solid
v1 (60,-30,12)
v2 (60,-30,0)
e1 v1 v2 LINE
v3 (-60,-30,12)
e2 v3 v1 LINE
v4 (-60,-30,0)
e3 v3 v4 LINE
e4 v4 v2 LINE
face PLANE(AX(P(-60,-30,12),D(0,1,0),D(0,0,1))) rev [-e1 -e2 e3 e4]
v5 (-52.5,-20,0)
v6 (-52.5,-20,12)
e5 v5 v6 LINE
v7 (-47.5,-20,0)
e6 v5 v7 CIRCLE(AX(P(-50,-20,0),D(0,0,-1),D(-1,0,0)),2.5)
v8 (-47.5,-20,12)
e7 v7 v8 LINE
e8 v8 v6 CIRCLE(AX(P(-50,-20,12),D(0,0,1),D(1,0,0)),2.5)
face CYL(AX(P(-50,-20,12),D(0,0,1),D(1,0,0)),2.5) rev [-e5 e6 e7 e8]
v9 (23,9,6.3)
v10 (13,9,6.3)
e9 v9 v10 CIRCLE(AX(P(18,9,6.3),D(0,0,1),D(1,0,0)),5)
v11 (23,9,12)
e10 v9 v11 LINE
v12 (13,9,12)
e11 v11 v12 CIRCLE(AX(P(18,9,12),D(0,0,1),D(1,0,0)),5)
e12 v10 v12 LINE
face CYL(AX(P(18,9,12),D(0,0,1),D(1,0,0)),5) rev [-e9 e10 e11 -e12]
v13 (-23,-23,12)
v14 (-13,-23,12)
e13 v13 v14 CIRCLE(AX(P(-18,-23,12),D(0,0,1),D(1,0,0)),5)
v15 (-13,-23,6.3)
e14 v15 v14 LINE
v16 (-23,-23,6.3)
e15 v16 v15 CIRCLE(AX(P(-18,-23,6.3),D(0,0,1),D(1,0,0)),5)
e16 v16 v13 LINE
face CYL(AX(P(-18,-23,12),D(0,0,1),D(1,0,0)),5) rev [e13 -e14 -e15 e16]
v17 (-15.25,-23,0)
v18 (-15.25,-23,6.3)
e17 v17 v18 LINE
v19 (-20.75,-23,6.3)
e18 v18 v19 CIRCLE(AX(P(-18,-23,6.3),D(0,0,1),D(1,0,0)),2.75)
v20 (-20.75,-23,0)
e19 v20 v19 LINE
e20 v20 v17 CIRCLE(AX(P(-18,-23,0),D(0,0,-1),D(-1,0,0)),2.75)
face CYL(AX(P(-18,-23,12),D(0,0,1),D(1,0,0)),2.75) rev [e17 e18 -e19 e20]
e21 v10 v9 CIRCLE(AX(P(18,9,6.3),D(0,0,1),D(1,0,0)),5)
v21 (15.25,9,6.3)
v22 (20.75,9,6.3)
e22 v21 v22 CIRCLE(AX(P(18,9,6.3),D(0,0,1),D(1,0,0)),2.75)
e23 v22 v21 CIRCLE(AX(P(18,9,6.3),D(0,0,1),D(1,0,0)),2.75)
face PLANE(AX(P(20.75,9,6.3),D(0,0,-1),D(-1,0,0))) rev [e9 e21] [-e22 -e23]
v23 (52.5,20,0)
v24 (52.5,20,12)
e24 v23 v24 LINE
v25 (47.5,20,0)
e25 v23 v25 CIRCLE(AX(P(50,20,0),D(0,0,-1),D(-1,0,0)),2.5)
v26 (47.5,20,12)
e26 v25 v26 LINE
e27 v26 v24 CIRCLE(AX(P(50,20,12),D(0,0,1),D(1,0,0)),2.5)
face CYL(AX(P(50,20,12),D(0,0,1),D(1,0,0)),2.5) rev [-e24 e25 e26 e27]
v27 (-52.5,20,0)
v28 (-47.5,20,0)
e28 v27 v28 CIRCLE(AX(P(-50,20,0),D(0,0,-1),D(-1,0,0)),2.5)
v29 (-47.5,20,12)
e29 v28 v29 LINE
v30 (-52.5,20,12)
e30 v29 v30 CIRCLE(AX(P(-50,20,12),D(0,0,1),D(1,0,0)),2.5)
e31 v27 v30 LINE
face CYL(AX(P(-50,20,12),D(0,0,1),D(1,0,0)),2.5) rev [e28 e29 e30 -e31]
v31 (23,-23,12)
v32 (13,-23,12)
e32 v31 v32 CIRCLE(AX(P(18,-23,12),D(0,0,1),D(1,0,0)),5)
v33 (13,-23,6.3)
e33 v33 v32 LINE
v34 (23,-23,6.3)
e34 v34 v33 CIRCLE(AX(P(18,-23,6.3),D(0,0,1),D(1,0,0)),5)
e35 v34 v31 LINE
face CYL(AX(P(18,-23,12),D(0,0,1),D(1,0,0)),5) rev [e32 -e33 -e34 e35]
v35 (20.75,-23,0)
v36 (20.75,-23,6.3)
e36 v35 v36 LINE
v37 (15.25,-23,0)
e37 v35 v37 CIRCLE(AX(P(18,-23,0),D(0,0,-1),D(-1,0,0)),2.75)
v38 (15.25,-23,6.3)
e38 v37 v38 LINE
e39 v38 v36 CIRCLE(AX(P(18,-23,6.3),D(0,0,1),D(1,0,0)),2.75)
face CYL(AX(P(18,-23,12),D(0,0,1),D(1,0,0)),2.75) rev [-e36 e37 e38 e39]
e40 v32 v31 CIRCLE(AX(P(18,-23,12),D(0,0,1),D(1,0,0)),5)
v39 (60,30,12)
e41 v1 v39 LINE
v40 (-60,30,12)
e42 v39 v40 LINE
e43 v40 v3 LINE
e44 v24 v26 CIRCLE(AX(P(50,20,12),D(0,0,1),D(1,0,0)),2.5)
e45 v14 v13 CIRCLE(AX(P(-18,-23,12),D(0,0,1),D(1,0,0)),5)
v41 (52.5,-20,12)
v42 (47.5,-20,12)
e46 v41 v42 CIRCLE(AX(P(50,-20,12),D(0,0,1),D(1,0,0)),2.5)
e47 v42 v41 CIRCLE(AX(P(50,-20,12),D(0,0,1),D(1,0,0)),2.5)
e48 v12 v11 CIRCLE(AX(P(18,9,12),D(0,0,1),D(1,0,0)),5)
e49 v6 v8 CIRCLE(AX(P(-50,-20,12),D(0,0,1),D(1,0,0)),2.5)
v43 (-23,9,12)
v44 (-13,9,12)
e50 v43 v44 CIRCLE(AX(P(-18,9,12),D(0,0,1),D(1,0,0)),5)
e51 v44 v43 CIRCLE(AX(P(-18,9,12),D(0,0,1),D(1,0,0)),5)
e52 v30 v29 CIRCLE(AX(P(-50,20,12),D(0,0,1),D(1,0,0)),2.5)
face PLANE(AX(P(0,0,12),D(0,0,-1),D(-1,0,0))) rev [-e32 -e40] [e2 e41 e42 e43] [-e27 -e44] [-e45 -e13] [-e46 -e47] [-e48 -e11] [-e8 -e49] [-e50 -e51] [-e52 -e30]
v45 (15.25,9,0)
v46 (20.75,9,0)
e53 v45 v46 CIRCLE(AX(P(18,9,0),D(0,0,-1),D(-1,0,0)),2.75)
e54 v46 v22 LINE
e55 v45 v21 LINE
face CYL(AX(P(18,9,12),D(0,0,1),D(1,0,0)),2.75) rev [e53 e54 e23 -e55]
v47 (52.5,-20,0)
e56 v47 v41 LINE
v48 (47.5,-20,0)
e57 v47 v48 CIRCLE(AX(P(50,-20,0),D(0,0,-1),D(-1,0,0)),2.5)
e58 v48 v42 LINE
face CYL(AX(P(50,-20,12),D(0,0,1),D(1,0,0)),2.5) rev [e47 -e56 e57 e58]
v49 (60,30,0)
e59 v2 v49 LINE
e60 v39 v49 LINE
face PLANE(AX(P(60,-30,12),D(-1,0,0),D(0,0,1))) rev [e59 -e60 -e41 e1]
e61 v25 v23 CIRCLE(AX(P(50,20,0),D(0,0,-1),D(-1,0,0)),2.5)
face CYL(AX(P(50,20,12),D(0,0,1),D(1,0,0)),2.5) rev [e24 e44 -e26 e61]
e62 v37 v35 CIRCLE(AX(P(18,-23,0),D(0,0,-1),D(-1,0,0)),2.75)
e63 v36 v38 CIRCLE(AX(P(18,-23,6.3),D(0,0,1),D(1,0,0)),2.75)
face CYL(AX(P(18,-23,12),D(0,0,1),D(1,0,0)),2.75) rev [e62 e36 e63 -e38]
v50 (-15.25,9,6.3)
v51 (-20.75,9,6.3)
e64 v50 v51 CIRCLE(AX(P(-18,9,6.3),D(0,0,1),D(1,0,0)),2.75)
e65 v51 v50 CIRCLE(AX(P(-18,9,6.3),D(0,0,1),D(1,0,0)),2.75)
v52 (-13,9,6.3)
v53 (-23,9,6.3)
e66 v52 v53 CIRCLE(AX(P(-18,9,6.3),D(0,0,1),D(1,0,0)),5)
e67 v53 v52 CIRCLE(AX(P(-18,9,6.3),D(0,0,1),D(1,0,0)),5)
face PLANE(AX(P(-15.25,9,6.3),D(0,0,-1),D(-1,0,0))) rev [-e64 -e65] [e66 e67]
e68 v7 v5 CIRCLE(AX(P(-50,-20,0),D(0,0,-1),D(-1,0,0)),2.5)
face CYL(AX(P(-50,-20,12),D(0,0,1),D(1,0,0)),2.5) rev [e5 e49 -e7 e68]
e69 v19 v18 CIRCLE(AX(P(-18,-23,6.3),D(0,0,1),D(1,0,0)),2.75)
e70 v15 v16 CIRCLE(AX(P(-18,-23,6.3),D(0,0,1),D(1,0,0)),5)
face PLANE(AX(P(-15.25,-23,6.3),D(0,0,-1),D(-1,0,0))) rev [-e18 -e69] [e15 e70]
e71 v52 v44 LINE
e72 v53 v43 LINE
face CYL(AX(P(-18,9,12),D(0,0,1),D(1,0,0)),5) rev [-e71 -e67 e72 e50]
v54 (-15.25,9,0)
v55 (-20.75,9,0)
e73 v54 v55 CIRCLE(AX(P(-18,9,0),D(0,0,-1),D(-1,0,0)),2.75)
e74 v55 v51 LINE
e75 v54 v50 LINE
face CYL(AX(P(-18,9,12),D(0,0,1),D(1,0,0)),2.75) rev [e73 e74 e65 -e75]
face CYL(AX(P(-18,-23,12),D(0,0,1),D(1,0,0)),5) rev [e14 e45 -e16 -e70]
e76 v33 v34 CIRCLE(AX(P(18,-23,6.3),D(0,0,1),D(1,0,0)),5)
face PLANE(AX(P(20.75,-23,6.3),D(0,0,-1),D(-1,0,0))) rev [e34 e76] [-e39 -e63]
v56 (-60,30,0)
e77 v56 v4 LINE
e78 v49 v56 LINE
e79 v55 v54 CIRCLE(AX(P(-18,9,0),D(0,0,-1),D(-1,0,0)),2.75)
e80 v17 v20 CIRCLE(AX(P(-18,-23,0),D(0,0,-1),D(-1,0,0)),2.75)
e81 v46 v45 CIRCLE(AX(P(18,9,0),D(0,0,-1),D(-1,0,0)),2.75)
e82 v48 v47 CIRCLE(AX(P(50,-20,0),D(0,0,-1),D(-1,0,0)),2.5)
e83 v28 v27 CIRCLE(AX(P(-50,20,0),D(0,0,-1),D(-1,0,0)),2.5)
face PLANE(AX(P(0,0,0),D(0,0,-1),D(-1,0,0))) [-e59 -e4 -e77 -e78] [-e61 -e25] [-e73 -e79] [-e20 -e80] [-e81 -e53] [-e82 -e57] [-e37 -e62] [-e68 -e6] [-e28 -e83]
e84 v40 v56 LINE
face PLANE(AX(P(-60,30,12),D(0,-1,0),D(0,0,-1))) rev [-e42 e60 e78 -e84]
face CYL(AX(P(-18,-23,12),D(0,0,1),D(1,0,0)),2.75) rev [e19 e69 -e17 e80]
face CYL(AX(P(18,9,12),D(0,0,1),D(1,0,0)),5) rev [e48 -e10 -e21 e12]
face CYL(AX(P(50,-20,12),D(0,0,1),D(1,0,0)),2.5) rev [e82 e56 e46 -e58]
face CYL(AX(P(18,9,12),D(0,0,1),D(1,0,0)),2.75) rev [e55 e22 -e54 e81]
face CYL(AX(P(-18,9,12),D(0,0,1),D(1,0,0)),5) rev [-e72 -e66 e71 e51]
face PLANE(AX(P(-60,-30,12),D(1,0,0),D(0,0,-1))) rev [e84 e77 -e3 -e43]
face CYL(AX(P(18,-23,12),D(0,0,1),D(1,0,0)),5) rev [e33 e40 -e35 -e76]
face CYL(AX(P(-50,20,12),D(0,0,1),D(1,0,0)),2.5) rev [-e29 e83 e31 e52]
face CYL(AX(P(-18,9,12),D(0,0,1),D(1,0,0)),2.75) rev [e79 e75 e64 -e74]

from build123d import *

# Parameters (mm, degrees)
SKETCH1_W                                         = 120
SKETCH1_H                                         = 60
SKETCH1_R                                         = 1.5
BOSS_EXTRUDE1_DEPTH                               = 12
HOLE_SIZE_PER_HEX_SOCKET_SCREW_TYPE_1_D           = 5.5
HOLE_SIZE_PER_HEX_SOCKET_SCREW_TYPE_1_DEPTH       = 18
HOLE_SIZE_PER_HEX_SOCKET_SCREW_TYPE_1_CBORE_D     = 10
HOLE_SIZE_PER_HEX_SOCKET_SCREW_TYPE_1_CBORE_DEPTH = 5.7
HOLE_SIZE_PER_HEX_SOCKET_SCREW_TYPE_1_TIP         = 1.652366702
M6_TAPPED_HOLE1_D                                 = 5
M6_TAPPED_HOLE1_DEPTH                             = 15
M6_TAPPED_HOLE1_TIP                               = 1.502151548


with BuildPart() as part:
    # Sketch1 → Boss-Extrude1 (new body)
    with BuildSketch(Plane.XY):
        Rectangle(SKETCH1_W, SKETCH1_H)
        with Locations((-50, 20)):
            Circle(SKETCH1_R, mode=Mode.SUBTRACT)
        with Locations((50, 20)):
            Circle(SKETCH1_R, mode=Mode.SUBTRACT)
        with Locations((50, -20)):
            Circle(SKETCH1_R, mode=Mode.SUBTRACT)
        with Locations((-50, -20)):
            Circle(SKETCH1_R, mode=Mode.SUBTRACT)
    extrude(amount=BOSS_EXTRUDE1_DEPTH)

    # Hole Size (per hex socket screw type)1
    with Locations(Plane(origin=(-18, 9, 12), x_dir=(1, 0, 0), z_dir=(0, 0, 1))):
        with Locations((0, 0), (36, 0), (0, -32), (36, -32)):
            CounterBoreHole(HOLE_SIZE_PER_HEX_SOCKET_SCREW_TYPE_1_D / 2, HOLE_SIZE_PER_HEX_SOCKET_SCREW_TYPE_1_CBORE_D / 2, HOLE_SIZE_PER_HEX_SOCKET_SCREW_TYPE_1_CBORE_DEPTH, depth=HOLE_SIZE_PER_HEX_SOCKET_SCREW_TYPE_1_DEPTH)
            with Locations((0, 0, -(HOLE_SIZE_PER_HEX_SOCKET_SCREW_TYPE_1_DEPTH + HOLE_SIZE_PER_HEX_SOCKET_SCREW_TYPE_1_TIP / 2))):  # 118° drill point
                Cone(0, HOLE_SIZE_PER_HEX_SOCKET_SCREW_TYPE_1_D / 2, HOLE_SIZE_PER_HEX_SOCKET_SCREW_TYPE_1_TIP, mode=Mode.SUBTRACT)

    # M6 Tapped Hole1
    with Locations(Plane.XY.offset(12)):
        with Locations((-50, 20), (-50, -20), (50, -20), (50, 20)):
            Hole(M6_TAPPED_HOLE1_D / 2, depth=M6_TAPPED_HOLE1_DEPTH)
            with Locations((0, 0, -(M6_TAPPED_HOLE1_DEPTH + M6_TAPPED_HOLE1_TIP / 2))):  # 118° drill point
                Cone(0, M6_TAPPED_HOLE1_D / 2, M6_TAPPED_HOLE1_TIP, mode=Mode.SUBTRACT)


solid = part.part
